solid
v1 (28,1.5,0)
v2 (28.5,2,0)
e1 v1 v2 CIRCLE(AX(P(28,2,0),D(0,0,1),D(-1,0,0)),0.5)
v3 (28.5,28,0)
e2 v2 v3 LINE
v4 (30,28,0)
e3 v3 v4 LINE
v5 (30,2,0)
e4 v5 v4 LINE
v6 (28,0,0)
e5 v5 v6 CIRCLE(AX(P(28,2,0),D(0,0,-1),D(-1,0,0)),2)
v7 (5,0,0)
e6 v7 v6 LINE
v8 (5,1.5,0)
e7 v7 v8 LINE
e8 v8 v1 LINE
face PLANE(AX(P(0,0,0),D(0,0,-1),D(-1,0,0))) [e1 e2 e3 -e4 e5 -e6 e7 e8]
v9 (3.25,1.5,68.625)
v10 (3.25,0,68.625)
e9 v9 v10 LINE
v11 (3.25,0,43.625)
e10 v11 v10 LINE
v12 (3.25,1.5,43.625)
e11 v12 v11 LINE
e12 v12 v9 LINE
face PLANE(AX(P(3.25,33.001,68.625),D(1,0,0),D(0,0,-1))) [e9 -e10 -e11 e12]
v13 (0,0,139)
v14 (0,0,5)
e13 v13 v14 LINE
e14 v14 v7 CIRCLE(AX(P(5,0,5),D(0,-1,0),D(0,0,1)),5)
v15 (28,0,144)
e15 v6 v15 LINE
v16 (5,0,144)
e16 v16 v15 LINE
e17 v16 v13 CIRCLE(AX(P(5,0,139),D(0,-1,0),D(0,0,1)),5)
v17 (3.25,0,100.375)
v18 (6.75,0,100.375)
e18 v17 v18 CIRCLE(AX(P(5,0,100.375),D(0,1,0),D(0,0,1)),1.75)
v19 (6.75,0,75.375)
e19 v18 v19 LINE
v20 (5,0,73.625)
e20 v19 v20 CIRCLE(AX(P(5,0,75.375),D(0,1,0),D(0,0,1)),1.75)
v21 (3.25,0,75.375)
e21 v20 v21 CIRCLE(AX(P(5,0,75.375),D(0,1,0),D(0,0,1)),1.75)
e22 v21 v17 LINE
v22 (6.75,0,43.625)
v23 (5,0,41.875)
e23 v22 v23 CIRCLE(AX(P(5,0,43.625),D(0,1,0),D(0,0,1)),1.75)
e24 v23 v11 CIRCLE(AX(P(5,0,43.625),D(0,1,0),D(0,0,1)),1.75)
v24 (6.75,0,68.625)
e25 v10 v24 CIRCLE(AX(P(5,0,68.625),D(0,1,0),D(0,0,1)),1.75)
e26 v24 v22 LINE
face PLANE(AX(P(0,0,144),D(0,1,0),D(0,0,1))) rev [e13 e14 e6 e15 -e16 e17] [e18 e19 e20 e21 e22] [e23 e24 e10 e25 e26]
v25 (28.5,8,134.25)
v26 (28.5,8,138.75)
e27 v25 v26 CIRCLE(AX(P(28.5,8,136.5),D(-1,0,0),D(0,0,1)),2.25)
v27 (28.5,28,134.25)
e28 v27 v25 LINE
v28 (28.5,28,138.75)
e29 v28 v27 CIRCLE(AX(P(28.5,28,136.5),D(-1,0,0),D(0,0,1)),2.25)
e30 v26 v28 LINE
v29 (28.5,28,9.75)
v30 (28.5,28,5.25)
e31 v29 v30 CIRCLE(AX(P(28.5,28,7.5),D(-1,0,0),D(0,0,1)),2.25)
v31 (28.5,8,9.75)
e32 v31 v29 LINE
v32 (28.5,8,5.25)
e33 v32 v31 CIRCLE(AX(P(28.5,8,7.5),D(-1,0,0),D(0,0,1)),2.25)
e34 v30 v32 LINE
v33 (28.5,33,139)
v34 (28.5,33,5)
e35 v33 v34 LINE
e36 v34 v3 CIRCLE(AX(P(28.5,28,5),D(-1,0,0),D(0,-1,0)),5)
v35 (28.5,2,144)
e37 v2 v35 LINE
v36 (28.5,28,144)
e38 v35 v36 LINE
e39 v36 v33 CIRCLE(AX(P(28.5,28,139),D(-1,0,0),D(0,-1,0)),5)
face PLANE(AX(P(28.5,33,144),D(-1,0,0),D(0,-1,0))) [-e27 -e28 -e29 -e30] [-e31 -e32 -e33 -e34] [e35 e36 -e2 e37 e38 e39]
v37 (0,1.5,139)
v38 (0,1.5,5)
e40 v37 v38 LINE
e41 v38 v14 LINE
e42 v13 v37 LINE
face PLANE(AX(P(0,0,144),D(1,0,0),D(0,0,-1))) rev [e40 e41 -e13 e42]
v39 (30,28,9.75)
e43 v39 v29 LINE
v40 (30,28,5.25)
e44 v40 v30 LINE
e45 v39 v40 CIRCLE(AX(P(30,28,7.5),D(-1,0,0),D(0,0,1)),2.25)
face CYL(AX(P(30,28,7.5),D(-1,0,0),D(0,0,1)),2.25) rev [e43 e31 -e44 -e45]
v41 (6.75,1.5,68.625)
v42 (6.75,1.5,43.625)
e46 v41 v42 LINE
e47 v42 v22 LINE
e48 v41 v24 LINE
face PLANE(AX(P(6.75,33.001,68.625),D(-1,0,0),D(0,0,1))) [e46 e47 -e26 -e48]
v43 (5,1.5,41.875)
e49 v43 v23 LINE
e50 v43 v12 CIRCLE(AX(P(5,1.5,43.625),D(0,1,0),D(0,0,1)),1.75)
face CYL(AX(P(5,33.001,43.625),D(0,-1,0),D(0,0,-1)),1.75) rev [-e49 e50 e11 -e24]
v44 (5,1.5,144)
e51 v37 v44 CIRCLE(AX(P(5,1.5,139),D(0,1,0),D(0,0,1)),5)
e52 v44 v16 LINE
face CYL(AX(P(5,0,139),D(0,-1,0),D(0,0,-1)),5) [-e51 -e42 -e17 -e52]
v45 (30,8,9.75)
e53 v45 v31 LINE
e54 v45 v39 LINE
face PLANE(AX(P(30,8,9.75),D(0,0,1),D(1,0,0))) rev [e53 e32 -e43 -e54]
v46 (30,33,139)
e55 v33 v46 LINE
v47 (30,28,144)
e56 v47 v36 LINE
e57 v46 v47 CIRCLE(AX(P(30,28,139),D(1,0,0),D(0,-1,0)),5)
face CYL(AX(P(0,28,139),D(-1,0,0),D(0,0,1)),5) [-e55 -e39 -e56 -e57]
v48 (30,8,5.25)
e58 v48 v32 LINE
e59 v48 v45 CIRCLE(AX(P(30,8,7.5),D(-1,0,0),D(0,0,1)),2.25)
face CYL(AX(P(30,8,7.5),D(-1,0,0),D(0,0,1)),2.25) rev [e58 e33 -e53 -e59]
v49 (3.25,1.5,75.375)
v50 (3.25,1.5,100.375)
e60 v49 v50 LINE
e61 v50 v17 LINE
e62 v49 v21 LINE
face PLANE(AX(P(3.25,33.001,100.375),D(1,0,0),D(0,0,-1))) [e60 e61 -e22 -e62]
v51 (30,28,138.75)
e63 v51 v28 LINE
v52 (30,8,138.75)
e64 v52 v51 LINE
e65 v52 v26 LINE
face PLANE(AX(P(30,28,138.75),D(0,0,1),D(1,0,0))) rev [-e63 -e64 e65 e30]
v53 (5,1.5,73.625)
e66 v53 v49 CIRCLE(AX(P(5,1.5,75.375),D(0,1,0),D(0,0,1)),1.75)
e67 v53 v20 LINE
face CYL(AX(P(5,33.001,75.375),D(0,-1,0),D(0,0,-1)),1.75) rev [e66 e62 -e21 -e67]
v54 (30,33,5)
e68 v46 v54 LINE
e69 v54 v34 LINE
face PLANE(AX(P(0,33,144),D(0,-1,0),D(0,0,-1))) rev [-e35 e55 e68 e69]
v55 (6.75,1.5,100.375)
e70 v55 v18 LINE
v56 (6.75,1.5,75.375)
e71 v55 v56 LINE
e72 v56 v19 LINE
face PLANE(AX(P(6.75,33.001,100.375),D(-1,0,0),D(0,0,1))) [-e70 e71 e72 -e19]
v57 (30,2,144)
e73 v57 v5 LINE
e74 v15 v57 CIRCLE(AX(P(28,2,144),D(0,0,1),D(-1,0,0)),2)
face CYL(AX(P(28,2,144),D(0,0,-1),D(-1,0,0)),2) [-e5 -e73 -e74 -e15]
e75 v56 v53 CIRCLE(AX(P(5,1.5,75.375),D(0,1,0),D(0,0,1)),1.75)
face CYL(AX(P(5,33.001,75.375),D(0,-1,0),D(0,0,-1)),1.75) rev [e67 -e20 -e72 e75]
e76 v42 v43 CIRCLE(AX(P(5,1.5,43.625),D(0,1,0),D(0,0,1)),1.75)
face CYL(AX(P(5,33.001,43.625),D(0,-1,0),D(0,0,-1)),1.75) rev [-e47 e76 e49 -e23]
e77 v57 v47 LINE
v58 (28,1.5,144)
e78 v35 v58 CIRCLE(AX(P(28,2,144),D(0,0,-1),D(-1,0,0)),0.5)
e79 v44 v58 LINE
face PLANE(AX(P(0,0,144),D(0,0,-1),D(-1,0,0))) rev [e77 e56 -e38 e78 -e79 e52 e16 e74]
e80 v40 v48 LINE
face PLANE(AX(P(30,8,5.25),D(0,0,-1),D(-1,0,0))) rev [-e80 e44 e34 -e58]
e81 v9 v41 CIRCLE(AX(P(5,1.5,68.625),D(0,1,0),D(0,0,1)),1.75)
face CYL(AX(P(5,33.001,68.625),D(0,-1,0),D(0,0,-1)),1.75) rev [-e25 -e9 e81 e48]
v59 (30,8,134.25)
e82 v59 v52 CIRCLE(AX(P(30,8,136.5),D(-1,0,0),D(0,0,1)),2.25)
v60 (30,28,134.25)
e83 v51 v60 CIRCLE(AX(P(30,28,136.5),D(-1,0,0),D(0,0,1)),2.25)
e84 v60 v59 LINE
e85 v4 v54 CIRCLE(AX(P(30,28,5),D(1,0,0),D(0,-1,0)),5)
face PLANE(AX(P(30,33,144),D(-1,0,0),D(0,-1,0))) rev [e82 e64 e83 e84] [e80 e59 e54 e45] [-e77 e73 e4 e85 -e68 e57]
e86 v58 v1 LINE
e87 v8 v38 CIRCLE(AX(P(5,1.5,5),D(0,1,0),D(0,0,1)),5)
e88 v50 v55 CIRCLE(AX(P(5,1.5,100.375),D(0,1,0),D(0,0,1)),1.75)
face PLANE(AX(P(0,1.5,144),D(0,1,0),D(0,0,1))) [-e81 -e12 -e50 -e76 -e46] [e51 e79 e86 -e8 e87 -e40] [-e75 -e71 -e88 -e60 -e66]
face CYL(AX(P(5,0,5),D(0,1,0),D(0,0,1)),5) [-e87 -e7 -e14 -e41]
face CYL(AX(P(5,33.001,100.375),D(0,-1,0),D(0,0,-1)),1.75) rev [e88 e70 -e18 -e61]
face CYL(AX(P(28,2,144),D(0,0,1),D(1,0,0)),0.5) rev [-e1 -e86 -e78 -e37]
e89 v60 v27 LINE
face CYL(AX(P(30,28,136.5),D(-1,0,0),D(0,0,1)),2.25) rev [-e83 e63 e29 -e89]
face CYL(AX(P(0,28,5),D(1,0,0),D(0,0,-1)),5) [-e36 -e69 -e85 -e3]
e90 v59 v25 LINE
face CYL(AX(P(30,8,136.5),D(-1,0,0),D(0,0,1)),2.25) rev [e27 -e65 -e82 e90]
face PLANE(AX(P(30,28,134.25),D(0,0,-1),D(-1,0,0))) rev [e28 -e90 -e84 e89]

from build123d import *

# Parameters (mm, degrees)
SKETCH_1_W          = 30
SKETCH_1_H          = 33
EXTRUDE_1_DEPTH     = 144
SHELL_1_T           = -1.5
FILLET_1_R          = 5
FILLET_2_R          = 0.5
FILLET_3_R          = 2
CUT_EXTRUDE_1_DEPTH = 198.864221121
CUT_EXTRUDE_2_REACH = 152.748
SKETCH_3_R          = 1.75
CUT_EXTRUDE_3_DEPTH = 1.5


with BuildPart() as part:
    # 草图1 → 凸台-拉伸1 (new body)
    with BuildSketch(Plane.XY):
        with Locations((15, 16.5)):
            Rectangle(SKETCH_1_W, SKETCH_1_H)
    extrude(amount=EXTRUDE_1_DEPTH)

    # 抽壳1
    shell_1_openings = [part.faces().sort_by_distance(p)[0] for p in [
        (15, 16.5, 144),
        (15, 16.5, 0),
        (15, 33, 72),
        (0, 16.5, 72),
    ]]
    offset(amount=SHELL_1_T, openings=shell_1_openings, kind=Kind.INTERSECTION)

    # 圆角1
    fillet_1_edges = [part.edges().sort_by_distance(p)[0] for p in [
        (29.25, 33, 144),
        (0, 0.75, 144),
        (29.25, 33, 0),
        (0, 0.75, 0),
    ]]
    fillet(fillet_1_edges, radius=FILLET_1_R)

    # 圆角2
    fillet_2_edges = [part.edges().sort_by_distance(p)[0] for p in [
        (28.5, 1.5, 72),
    ]]
    fillet(fillet_2_edges, radius=FILLET_2_R)

    # 圆角3
    fillet_3_edges = [part.edges().sort_by_distance(p)[0] for p in [
        (30, 0, 72),
    ]]
    fillet(fillet_3_edges, radius=FILLET_3_R)

    # 草图2 → 切除-拉伸1 (cut, through all)
    with BuildSketch(Plane(origin=(28.5, 0, -49), x_dir=(0, 0, 1), z_dir=(-1, 0, 0))):
        with BuildLine():
            Line((54.25, 8), (54.25, 28))
            ThreePointArc((54.25, 28), (56.5, 30.25), (58.75, 28))
            Line((58.75, 28), (58.75, 8))
            ThreePointArc((58.75, 8), (56.5, 5.75), (54.25, 8))
        make_face()
        with BuildLine():
            Line((187.75, 28), (187.75, 8))
            ThreePointArc((187.75, 8), (185.5, 5.75), (183.25, 8))
            Line((183.25, 8), (183.25, 28))
            ThreePointArc((183.25, 28), (185.5, 30.25), (187.75, 28))
        make_face()
    extrude(amount=-CUT_EXTRUDE_1_DEPTH, mode=Mode.SUBTRACT)

    # 草图3 → 切除-拉伸2 (cut, up to next)
    with BuildSketch(Plane(origin=(0, 0, 0), x_dir=(1, 0, 0), z_dir=(0, 1, 0)), mode=Mode.PRIVATE) as cut_extrude_2_sk1:
        with Locations(Location((5, -87.875, 0), (0, 0, 270))):
            Circle(SKETCH_3_R)
    cut_extrude_2_tool1 = extrude(cut_extrude_2_sk1.sketch, amount=CUT_EXTRUDE_2_REACH, mode=Mode.PRIVATE) & part.part
    # 草图3 → 切除-拉伸2 (cut, up to next)
    with BuildSketch(Plane(origin=(0, 0, 0), x_dir=(1, 0, 0), z_dir=(0, 1, 0)), mode=Mode.PRIVATE) as cut_extrude_2_sk2:
        with Locations(Location((5, -56.125, 0), (0, 0, 270))):
            Circle(SKETCH_3_R)
    cut_extrude_2_tool2 = extrude(cut_extrude_2_sk2.sketch, amount=CUT_EXTRUDE_2_REACH, mode=Mode.PRIVATE) & part.part
    add(cut_extrude_2_tool1.solids().sort_by_distance((5, 0, 87.875))[0], mode=Mode.SUBTRACT)
    add(cut_extrude_2_tool2.solids().sort_by_distance((5, 0, 56.125))[0], mode=Mode.SUBTRACT)

    # 草图4 → 切除-拉伸3 (cut)
    with BuildSketch(Plane(origin=(0, 0, 0), x_dir=(1, 0, 0), z_dir=(0, 1, 0))):
        with BuildLine():
            Line((3.25, -100.375), (3.25, -75.375))
            ThreePointArc((3.25, -75.375), (5, -73.625), (6.75, -75.375))
            Line((6.75, -75.375), (6.75, -100.375))
            ThreePointArc((6.75, -100.375), (5, -102.125), (3.25, -100.375))
        make_face()
        with BuildLine():
            Line((3.25, -68.625), (3.25, -43.625))
            ThreePointArc((3.25, -43.625), (5, -41.875), (6.75, -43.625))
            Line((6.75, -43.625), (6.75, -68.625))
            ThreePointArc((6.75, -68.625), (5, -70.375), (3.25, -68.625))
        make_face()
    extrude(amount=CUT_EXTRUDE_3_DEPTH, mode=Mode.SUBTRACT)


solid = part.part
